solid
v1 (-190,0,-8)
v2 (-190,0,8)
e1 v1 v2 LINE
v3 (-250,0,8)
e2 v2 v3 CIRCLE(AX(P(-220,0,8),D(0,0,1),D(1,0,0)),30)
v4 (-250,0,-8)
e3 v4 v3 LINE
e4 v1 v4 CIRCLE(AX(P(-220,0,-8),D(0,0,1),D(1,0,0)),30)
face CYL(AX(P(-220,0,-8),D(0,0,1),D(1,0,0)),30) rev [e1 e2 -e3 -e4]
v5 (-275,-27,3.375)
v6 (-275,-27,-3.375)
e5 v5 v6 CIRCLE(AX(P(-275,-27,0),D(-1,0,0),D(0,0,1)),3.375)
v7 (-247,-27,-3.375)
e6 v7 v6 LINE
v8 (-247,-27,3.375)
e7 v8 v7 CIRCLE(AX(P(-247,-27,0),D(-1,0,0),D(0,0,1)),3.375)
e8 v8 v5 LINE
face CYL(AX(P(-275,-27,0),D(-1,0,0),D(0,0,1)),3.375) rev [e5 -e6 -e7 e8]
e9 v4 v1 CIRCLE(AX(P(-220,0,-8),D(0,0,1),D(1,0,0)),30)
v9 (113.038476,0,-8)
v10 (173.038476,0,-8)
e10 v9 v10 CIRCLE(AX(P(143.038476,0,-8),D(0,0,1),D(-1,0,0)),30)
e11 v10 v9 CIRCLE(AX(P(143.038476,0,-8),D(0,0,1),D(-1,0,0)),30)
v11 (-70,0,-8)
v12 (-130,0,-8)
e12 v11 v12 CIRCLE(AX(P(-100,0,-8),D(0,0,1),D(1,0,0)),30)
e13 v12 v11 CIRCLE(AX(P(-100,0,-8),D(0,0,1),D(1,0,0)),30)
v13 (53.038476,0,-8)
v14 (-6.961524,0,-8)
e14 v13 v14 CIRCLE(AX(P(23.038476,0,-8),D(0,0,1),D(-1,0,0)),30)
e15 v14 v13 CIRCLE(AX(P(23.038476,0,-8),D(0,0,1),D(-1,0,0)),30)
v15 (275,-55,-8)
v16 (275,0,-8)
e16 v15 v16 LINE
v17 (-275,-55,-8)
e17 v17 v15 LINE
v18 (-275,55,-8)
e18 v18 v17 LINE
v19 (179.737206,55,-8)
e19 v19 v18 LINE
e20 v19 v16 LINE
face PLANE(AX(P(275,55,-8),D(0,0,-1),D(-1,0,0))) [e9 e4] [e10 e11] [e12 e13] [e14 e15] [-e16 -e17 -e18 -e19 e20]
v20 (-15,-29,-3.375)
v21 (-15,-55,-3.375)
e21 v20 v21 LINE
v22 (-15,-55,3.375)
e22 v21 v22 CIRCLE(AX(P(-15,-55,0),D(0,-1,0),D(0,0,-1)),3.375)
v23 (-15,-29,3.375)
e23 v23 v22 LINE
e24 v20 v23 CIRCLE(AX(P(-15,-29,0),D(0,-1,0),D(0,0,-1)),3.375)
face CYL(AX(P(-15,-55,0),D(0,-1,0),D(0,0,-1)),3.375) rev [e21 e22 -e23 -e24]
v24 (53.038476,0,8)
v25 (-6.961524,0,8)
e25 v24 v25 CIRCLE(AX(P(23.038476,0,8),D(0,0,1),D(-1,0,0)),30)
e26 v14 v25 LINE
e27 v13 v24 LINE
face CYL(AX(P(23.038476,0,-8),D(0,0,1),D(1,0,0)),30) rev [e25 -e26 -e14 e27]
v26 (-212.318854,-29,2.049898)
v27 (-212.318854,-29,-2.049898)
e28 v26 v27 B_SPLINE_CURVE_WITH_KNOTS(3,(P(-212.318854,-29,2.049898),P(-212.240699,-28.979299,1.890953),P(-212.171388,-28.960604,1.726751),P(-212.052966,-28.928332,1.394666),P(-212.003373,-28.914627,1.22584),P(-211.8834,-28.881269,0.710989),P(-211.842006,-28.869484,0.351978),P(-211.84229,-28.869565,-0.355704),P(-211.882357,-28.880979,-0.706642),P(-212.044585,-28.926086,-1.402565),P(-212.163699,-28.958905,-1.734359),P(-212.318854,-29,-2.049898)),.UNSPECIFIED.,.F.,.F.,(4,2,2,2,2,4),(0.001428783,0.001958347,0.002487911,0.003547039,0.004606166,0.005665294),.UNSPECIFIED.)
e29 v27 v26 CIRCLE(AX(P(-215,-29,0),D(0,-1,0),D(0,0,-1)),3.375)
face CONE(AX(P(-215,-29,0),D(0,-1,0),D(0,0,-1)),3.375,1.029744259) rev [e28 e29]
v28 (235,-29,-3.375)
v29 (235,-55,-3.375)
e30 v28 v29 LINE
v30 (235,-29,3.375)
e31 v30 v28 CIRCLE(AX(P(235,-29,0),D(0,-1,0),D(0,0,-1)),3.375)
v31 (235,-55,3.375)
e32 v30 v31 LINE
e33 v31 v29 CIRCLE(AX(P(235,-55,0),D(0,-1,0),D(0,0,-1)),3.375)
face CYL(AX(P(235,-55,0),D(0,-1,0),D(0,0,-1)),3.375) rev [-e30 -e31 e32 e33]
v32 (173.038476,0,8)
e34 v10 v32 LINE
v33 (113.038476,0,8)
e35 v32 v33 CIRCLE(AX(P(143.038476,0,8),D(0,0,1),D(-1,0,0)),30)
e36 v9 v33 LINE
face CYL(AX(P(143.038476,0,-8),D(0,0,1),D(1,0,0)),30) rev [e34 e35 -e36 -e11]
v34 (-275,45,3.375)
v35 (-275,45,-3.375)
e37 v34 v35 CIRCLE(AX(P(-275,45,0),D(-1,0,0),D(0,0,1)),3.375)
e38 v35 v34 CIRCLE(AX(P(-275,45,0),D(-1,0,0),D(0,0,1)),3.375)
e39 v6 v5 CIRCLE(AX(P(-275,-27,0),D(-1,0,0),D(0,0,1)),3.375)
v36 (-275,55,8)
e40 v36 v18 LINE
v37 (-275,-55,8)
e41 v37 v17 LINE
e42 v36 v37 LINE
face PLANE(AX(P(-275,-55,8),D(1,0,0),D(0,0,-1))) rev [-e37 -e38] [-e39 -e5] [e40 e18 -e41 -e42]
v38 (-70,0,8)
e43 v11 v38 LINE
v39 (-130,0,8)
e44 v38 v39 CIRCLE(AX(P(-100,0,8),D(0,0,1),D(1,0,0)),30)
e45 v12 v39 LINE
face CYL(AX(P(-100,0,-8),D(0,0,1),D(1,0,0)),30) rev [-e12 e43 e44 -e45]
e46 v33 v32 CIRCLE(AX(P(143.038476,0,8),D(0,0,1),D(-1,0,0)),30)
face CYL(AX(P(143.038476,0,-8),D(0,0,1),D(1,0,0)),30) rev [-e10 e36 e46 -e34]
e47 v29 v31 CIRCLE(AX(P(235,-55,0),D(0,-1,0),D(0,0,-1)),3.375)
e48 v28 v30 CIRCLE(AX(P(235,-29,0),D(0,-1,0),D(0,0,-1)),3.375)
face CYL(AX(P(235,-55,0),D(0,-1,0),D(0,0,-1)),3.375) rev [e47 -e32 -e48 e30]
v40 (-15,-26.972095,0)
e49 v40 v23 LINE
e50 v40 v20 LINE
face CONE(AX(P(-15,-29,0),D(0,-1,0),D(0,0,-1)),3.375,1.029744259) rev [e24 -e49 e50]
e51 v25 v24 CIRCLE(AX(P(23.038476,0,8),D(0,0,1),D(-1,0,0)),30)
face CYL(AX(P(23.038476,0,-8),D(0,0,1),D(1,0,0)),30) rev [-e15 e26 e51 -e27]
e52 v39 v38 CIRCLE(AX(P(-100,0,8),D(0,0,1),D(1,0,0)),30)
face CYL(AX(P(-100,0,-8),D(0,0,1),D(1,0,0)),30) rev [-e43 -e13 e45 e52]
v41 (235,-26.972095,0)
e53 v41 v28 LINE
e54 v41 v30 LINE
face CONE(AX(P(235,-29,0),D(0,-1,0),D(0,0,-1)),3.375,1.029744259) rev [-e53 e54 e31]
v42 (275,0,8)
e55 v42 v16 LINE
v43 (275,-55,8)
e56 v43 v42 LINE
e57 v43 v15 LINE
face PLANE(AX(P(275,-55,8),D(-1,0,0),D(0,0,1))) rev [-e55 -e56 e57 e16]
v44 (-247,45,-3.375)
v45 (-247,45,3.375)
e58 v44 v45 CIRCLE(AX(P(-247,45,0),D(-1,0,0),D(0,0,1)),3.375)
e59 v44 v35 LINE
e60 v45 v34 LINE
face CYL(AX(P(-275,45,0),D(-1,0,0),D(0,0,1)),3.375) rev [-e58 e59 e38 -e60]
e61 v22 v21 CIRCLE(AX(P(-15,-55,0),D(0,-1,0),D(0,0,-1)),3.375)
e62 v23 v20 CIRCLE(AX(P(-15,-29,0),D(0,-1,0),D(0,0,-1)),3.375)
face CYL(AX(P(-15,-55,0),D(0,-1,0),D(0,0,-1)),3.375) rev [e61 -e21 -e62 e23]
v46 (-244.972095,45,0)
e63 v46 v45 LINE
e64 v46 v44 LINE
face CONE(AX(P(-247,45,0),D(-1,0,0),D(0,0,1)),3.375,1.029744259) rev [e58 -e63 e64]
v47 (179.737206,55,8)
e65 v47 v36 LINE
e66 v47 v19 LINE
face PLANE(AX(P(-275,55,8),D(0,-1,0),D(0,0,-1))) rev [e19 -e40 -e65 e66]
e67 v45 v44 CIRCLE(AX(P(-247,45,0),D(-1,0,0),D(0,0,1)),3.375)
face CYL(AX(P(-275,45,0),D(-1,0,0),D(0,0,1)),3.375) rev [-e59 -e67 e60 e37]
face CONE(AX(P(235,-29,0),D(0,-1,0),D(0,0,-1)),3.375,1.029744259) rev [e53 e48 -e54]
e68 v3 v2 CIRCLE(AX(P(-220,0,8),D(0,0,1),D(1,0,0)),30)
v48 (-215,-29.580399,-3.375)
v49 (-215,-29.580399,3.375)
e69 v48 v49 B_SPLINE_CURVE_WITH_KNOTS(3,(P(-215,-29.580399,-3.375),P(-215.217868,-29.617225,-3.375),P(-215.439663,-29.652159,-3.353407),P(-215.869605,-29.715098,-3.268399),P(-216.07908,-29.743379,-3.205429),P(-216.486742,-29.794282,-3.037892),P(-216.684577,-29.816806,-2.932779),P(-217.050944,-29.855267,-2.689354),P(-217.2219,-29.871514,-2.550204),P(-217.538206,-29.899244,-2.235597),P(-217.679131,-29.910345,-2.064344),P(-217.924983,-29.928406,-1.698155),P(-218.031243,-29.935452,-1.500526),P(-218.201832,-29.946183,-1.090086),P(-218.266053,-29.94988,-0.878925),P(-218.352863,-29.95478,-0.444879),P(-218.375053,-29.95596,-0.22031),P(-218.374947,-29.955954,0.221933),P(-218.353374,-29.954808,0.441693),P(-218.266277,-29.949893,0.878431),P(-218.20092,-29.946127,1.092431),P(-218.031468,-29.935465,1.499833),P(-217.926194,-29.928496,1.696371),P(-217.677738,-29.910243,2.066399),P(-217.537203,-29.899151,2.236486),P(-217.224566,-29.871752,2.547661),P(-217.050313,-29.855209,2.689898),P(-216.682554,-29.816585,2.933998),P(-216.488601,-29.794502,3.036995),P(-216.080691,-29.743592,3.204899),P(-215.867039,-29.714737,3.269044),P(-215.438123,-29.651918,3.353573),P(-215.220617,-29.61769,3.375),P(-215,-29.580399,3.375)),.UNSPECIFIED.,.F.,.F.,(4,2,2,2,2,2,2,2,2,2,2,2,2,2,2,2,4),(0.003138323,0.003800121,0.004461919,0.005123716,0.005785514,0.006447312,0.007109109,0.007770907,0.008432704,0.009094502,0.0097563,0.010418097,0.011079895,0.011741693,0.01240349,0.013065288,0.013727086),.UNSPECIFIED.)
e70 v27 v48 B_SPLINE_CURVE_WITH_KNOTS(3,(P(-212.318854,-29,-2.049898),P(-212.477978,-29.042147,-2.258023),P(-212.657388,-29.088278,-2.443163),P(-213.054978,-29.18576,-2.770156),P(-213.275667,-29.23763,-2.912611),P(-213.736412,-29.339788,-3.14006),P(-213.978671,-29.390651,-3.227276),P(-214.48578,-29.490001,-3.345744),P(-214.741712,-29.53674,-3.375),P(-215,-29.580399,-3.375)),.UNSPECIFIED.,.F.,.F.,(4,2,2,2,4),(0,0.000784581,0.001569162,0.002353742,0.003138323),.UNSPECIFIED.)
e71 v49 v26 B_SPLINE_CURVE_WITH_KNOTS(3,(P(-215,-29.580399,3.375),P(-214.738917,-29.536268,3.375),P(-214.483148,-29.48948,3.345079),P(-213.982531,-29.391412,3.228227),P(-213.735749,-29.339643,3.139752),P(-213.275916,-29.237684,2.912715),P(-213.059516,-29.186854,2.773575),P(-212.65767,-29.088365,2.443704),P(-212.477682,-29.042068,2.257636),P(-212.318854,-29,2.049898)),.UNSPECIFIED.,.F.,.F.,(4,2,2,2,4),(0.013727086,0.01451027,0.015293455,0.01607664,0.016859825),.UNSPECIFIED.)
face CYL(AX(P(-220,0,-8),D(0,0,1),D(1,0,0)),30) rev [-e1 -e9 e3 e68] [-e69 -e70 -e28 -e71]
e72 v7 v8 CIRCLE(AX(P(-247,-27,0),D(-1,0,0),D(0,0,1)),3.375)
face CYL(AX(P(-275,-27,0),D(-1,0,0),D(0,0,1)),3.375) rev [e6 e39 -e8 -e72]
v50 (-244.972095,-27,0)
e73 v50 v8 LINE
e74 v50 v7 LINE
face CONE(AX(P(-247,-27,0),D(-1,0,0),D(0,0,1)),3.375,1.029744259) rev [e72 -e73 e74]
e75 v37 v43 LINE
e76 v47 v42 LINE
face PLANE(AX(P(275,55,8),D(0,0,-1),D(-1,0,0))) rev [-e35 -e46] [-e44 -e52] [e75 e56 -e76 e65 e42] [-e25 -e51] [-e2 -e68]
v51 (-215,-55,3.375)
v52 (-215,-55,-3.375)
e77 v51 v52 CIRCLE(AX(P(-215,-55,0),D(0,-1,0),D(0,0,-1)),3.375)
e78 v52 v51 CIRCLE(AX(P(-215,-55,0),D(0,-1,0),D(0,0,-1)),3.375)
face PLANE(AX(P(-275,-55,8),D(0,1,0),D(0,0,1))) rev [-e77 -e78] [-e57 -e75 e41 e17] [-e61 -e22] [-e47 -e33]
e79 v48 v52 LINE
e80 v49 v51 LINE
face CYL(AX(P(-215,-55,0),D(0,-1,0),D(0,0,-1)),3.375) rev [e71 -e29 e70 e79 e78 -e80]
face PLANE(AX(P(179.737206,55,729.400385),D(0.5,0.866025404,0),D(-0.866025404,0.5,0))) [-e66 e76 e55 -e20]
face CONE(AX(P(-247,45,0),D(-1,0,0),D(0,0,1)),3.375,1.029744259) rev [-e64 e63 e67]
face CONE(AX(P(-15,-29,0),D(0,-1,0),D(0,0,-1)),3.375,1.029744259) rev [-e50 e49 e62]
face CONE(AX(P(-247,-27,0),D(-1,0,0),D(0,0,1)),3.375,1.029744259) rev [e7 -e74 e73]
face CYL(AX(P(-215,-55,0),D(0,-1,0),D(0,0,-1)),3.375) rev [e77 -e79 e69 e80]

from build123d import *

# Parameters (mm, degrees)
SKETCH_1_W               = 550
SKETCH_1_H               = 110
EXTRUDE_1_DEPTH          = 8
CUT_EXTRUDE_4_DEPTH      = 281.902118184
CUT_EXTRUDE_4_DEPTH_BACK = 281.902118184
HOLE1_D                  = 6.75
HOLE1_DEPTH              = 26
HOLE1_TIP                = 2.027904589
HOLE11_D                 = 6.75
HOLE11_DEPTH             = 28
HOLE11_TIP               = 2.027904589
SKETCH_10_R              = 30
CUT_EXTRUDE_5_DEPTH      = 281.902118184


with BuildPart() as part:
    # 草图1 → 凸台-拉伸1 (new, symmetric)
    with BuildSketch(Plane.XY):
        Rectangle(SKETCH_1_W, SKETCH_1_H)
    extrude(amount=EXTRUDE_1_DEPTH, both=True)

    # 草图9 → 切除-拉伸4 (cut, two sides: drawn at the far end of the back side and taken through both)
    with BuildSketch(Plane.XY.offset(8).offset(-CUT_EXTRUDE_4_DEPTH_BACK)):
        Polygon((-786.302283658, 612.743159162), (179.737205584, 55), (275, 0), (1241.039489242, -557.743159162), (2356.525807565, 1374.335819322), (329.184034665, 2544.822137646), align=None)
    extrude(amount=CUT_EXTRUDE_4_DEPTH + CUT_EXTRUDE_4_DEPTH_BACK, mode=Mode.SUBTRACT)

    # Hole1
    with Locations(Plane(origin=(-134.213455343, -55, 9.167765698), x_dir=(1, 0, 0), z_dir=(0, -1, 0))):
        with Locations((-80.786544657, -9.167765698), (119.213455343, -9.167765698), (369.213455343, -9.167765698)):
            Hole(HOLE1_D / 2, depth=HOLE1_DEPTH)
            with Locations((0, 0, -(HOLE1_DEPTH + HOLE1_TIP / 2))):  # 118° drill point
                Cone(0, HOLE1_D / 2, HOLE1_TIP, mode=Mode.SUBTRACT)

    # Hole11
    with Locations(Plane(origin=(-275, -17.832234302, -14.213455343), x_dir=(0, 0, 1), z_dir=(-1, 0, 0))):
        with Locations((14.213455343, -9.167765698), (14.213455343, 62.832234302)):
            Hole(HOLE11_D / 2, depth=HOLE11_DEPTH)
            with Locations((0, 0, -(HOLE11_DEPTH + HOLE11_TIP / 2))):  # 118° drill point
                Cone(0, HOLE11_D / 2, HOLE11_TIP, mode=Mode.SUBTRACT)

    # 草图10 → 切除-拉伸5 (cut, through all)
    with BuildSketch(Plane.XY.offset(8)):
        with Locations((-220, 0)):
            Circle(SKETCH_10_R)
        with Locations((-100, 0)):
            Circle(SKETCH_10_R)
        with Locations(Location((23.038475773, 0, 0), (0, 0, 180))):
            Circle(SKETCH_10_R)
        with Locations(Location((143.038475773, 0, 0), (0, 0, 180))):
            Circle(SKETCH_10_R)
    extrude(amount=-CUT_EXTRUDE_5_DEPTH, mode=Mode.SUBTRACT)


solid = part.part
